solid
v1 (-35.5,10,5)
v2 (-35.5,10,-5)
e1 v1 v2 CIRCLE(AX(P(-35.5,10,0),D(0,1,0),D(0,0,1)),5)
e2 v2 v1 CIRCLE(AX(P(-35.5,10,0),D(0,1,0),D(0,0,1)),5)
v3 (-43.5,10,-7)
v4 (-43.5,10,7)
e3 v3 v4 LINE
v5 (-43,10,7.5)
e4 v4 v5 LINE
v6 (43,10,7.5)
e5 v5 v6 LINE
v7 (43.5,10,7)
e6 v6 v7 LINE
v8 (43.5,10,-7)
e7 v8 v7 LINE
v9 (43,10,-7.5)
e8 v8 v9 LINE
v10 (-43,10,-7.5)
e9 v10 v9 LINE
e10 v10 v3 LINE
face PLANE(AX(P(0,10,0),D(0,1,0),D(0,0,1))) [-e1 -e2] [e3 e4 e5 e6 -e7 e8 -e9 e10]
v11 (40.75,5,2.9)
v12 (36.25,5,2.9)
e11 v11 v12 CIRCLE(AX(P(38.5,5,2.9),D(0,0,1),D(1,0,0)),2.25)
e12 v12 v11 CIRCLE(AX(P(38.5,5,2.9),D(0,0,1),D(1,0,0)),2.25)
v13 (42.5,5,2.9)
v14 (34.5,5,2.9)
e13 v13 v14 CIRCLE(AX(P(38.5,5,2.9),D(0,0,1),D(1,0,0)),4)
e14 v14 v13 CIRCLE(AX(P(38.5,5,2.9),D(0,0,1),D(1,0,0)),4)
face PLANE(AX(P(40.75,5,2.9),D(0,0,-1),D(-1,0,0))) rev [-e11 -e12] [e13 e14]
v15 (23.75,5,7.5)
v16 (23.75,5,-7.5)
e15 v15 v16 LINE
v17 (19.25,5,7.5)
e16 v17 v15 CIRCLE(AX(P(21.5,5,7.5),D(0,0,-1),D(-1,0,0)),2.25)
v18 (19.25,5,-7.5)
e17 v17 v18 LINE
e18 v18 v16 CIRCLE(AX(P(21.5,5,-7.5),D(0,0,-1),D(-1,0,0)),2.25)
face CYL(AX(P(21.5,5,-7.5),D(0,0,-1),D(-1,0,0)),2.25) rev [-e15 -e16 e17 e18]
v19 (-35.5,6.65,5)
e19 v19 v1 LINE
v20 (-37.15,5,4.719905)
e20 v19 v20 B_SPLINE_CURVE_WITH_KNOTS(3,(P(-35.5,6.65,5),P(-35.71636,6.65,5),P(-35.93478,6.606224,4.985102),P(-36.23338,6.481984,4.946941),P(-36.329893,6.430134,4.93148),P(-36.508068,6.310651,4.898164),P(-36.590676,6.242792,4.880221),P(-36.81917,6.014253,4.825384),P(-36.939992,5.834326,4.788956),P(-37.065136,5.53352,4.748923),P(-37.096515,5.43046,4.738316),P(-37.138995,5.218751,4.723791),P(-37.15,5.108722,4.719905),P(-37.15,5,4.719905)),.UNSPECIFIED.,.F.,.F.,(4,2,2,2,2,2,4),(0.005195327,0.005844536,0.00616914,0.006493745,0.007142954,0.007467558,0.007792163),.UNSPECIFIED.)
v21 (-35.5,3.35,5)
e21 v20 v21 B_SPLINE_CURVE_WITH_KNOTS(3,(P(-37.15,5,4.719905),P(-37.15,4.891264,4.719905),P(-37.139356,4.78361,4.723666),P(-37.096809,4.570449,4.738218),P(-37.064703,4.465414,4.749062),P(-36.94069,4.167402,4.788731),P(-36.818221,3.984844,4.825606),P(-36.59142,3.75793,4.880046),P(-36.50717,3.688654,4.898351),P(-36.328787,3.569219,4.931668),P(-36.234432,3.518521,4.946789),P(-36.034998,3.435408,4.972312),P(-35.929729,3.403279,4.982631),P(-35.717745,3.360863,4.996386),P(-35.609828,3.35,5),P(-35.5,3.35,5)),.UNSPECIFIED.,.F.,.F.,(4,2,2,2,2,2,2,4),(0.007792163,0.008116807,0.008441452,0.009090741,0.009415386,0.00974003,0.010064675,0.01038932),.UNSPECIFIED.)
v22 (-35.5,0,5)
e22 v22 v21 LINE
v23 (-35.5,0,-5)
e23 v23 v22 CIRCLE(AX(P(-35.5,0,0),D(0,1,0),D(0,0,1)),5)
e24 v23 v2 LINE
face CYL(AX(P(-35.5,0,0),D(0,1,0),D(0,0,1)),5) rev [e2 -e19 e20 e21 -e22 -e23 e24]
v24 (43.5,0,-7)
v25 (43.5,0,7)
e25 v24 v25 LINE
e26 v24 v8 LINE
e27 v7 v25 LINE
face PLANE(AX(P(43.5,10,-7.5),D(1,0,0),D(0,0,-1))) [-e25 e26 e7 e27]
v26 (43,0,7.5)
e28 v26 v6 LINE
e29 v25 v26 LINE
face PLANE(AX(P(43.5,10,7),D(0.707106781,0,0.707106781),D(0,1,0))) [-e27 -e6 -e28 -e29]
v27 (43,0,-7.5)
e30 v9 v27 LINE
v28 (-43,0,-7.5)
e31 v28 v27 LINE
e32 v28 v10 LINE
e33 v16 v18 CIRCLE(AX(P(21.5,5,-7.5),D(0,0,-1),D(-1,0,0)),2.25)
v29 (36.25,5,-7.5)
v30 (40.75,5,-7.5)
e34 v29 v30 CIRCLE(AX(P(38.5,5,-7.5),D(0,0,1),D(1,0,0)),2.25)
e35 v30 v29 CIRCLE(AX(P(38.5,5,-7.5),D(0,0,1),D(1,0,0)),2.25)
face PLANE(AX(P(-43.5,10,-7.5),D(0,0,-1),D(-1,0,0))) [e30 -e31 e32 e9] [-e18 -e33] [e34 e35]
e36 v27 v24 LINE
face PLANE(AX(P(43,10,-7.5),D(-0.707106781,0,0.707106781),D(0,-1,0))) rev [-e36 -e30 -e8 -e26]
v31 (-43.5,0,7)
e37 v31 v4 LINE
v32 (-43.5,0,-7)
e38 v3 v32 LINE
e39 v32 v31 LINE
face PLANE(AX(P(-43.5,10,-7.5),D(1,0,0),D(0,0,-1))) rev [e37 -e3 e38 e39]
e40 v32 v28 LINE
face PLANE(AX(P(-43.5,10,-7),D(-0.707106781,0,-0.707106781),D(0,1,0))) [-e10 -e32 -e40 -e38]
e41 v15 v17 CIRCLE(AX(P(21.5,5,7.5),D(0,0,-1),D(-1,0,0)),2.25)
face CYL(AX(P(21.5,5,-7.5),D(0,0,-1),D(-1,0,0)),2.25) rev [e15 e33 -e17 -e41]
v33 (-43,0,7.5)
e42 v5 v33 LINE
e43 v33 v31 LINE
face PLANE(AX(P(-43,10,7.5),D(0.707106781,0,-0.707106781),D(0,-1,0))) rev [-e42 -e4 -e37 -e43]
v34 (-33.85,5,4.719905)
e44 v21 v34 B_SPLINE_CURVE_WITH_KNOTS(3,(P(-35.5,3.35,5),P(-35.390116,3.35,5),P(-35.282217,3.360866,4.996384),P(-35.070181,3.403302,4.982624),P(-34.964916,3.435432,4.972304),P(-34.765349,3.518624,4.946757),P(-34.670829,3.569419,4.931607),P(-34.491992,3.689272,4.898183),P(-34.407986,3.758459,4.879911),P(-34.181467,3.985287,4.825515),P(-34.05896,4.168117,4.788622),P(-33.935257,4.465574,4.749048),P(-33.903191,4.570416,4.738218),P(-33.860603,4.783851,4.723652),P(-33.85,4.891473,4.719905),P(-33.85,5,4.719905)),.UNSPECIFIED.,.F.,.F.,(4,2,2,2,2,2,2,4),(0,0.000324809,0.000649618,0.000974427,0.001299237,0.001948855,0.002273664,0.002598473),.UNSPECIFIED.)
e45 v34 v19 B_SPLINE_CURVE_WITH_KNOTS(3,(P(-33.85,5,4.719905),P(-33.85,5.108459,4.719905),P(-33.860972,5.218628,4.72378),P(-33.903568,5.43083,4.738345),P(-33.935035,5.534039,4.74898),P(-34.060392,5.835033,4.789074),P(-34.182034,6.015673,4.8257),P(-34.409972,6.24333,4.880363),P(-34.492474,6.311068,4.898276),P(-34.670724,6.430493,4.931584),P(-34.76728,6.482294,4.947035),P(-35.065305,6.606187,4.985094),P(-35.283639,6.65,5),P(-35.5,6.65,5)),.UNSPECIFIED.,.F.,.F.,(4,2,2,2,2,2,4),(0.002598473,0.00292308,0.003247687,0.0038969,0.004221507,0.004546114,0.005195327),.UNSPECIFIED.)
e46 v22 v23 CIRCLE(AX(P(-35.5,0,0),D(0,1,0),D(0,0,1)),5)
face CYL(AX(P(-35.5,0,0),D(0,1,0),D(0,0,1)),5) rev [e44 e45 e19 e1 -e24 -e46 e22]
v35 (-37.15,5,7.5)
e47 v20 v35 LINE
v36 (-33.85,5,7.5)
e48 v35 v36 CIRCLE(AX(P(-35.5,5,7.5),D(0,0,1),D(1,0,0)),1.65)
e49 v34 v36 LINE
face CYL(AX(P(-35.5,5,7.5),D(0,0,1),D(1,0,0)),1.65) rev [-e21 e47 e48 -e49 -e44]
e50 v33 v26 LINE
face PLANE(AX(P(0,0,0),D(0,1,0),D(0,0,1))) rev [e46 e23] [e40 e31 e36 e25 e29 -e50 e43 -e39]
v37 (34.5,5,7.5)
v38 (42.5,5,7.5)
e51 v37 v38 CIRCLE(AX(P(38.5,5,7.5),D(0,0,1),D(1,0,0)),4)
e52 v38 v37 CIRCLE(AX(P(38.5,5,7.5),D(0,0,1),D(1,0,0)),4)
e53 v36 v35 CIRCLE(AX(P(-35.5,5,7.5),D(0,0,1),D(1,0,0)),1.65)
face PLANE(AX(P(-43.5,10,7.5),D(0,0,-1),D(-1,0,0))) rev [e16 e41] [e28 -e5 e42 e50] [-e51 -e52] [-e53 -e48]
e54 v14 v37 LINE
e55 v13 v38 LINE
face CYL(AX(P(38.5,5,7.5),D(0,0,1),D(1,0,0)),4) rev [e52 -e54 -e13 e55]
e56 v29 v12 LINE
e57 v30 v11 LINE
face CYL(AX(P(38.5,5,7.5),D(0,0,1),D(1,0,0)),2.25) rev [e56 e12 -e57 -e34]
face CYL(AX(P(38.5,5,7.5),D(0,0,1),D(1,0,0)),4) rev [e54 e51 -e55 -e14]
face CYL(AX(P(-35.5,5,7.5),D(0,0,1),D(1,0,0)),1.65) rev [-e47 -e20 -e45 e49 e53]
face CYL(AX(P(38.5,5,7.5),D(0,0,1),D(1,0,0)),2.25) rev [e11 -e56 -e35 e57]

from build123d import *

# Parameters (mm, degrees)
SKETCH1_W                                            = 87
SKETCH1_H                                            = 15
BOSS_EXTRUDE1_DEPTH                                  = 10
SKETCH2_R                                            = 5
CUT_EXTRUDE1_DEPTH                                   = 46.260357931
F_4_5_4_5_DIAMETER_HOLE2_D                           = 4.5
CBORE_FOR_M4_SLOTTED_CHEESE_HEAD_SCREWS2_D           = 4.5
CBORE_FOR_M4_SLOTTED_CHEESE_HEAD_SCREWS2_CBORE_D     = 8
CBORE_FOR_M4_SLOTTED_CHEESE_HEAD_SCREWS2_CBORE_DEPTH = 4.6
CHAMFER1_SIZE                                        = 0.5
M4_TAPPED_HOLE2_D                                    = 3.3
M4_TAPPED_HOLE2_DEPTH                                = 8
M4_TAPPED_HOLE2_TIP                                  = 0.991420021


with BuildPart() as part:
    # Sketch1 → Boss-Extrude1 (new body)
    with BuildSketch(Plane(origin=(0, 0, 0), x_dir=(1, 0, 0), z_dir=(0, 1, 0))):
        Rectangle(SKETCH1_W, SKETCH1_H)
    extrude(amount=BOSS_EXTRUDE1_DEPTH)

    # Sketch2 → Cut-Extrude1 (cut, through all)
    with BuildSketch(Plane(origin=(0, 10, 0), x_dir=(1, 0, 0), z_dir=(0, 1, 0))):
        with Locations(Location((-35.5, 0, 0), (0, 0, 270))):
            Circle(SKETCH2_R)
    extrude(amount=-CUT_EXTRUDE1_DEPTH, mode=Mode.SUBTRACT)

    # Ø4.5 (4.5) Diameter Hole2 (through all)
    with Locations(Plane(origin=(0, 0, -7.5), x_dir=(-1, 0, 0), z_dir=(0, 0, -1))):
        with Locations((-21.5, 5)):
            Hole(F_4_5_4_5_DIAMETER_HOLE2_D / 2)

    # CBORE for M4 Slotted cheese head screws2 (through all)
    with Locations(Plane.XY.offset(7.5)):
        with Locations((38.5, 5)):
            CounterBoreHole(CBORE_FOR_M4_SLOTTED_CHEESE_HEAD_SCREWS2_D / 2, CBORE_FOR_M4_SLOTTED_CHEESE_HEAD_SCREWS2_CBORE_D / 2, CBORE_FOR_M4_SLOTTED_CHEESE_HEAD_SCREWS2_CBORE_DEPTH)

    # Chamfer1
    chamfer1_edges = [part.edges().sort_by_distance(p)[0] for p in [
        (-43.5, 5, -7.5),
        (43.5, 5, -7.5),
        (43.5, 5, 7.5),
        (-43.5, 5, 7.5),
    ]]
    chamfer(chamfer1_edges, length=CHAMFER1_SIZE)

    # M4 Tapped Hole2
    with Locations(Plane.XY.offset(7.5)):
        with Locations((-35.5, 5)):
            Hole(M4_TAPPED_HOLE2_D / 2, depth=M4_TAPPED_HOLE2_DEPTH)
            with Locations((0, 0, -(M4_TAPPED_HOLE2_DEPTH + M4_TAPPED_HOLE2_TIP / 2))):  # 118° drill point
                Cone(0, M4_TAPPED_HOLE2_D / 2, M4_TAPPED_HOLE2_TIP, mode=Mode.SUBTRACT)


solid = part.part
